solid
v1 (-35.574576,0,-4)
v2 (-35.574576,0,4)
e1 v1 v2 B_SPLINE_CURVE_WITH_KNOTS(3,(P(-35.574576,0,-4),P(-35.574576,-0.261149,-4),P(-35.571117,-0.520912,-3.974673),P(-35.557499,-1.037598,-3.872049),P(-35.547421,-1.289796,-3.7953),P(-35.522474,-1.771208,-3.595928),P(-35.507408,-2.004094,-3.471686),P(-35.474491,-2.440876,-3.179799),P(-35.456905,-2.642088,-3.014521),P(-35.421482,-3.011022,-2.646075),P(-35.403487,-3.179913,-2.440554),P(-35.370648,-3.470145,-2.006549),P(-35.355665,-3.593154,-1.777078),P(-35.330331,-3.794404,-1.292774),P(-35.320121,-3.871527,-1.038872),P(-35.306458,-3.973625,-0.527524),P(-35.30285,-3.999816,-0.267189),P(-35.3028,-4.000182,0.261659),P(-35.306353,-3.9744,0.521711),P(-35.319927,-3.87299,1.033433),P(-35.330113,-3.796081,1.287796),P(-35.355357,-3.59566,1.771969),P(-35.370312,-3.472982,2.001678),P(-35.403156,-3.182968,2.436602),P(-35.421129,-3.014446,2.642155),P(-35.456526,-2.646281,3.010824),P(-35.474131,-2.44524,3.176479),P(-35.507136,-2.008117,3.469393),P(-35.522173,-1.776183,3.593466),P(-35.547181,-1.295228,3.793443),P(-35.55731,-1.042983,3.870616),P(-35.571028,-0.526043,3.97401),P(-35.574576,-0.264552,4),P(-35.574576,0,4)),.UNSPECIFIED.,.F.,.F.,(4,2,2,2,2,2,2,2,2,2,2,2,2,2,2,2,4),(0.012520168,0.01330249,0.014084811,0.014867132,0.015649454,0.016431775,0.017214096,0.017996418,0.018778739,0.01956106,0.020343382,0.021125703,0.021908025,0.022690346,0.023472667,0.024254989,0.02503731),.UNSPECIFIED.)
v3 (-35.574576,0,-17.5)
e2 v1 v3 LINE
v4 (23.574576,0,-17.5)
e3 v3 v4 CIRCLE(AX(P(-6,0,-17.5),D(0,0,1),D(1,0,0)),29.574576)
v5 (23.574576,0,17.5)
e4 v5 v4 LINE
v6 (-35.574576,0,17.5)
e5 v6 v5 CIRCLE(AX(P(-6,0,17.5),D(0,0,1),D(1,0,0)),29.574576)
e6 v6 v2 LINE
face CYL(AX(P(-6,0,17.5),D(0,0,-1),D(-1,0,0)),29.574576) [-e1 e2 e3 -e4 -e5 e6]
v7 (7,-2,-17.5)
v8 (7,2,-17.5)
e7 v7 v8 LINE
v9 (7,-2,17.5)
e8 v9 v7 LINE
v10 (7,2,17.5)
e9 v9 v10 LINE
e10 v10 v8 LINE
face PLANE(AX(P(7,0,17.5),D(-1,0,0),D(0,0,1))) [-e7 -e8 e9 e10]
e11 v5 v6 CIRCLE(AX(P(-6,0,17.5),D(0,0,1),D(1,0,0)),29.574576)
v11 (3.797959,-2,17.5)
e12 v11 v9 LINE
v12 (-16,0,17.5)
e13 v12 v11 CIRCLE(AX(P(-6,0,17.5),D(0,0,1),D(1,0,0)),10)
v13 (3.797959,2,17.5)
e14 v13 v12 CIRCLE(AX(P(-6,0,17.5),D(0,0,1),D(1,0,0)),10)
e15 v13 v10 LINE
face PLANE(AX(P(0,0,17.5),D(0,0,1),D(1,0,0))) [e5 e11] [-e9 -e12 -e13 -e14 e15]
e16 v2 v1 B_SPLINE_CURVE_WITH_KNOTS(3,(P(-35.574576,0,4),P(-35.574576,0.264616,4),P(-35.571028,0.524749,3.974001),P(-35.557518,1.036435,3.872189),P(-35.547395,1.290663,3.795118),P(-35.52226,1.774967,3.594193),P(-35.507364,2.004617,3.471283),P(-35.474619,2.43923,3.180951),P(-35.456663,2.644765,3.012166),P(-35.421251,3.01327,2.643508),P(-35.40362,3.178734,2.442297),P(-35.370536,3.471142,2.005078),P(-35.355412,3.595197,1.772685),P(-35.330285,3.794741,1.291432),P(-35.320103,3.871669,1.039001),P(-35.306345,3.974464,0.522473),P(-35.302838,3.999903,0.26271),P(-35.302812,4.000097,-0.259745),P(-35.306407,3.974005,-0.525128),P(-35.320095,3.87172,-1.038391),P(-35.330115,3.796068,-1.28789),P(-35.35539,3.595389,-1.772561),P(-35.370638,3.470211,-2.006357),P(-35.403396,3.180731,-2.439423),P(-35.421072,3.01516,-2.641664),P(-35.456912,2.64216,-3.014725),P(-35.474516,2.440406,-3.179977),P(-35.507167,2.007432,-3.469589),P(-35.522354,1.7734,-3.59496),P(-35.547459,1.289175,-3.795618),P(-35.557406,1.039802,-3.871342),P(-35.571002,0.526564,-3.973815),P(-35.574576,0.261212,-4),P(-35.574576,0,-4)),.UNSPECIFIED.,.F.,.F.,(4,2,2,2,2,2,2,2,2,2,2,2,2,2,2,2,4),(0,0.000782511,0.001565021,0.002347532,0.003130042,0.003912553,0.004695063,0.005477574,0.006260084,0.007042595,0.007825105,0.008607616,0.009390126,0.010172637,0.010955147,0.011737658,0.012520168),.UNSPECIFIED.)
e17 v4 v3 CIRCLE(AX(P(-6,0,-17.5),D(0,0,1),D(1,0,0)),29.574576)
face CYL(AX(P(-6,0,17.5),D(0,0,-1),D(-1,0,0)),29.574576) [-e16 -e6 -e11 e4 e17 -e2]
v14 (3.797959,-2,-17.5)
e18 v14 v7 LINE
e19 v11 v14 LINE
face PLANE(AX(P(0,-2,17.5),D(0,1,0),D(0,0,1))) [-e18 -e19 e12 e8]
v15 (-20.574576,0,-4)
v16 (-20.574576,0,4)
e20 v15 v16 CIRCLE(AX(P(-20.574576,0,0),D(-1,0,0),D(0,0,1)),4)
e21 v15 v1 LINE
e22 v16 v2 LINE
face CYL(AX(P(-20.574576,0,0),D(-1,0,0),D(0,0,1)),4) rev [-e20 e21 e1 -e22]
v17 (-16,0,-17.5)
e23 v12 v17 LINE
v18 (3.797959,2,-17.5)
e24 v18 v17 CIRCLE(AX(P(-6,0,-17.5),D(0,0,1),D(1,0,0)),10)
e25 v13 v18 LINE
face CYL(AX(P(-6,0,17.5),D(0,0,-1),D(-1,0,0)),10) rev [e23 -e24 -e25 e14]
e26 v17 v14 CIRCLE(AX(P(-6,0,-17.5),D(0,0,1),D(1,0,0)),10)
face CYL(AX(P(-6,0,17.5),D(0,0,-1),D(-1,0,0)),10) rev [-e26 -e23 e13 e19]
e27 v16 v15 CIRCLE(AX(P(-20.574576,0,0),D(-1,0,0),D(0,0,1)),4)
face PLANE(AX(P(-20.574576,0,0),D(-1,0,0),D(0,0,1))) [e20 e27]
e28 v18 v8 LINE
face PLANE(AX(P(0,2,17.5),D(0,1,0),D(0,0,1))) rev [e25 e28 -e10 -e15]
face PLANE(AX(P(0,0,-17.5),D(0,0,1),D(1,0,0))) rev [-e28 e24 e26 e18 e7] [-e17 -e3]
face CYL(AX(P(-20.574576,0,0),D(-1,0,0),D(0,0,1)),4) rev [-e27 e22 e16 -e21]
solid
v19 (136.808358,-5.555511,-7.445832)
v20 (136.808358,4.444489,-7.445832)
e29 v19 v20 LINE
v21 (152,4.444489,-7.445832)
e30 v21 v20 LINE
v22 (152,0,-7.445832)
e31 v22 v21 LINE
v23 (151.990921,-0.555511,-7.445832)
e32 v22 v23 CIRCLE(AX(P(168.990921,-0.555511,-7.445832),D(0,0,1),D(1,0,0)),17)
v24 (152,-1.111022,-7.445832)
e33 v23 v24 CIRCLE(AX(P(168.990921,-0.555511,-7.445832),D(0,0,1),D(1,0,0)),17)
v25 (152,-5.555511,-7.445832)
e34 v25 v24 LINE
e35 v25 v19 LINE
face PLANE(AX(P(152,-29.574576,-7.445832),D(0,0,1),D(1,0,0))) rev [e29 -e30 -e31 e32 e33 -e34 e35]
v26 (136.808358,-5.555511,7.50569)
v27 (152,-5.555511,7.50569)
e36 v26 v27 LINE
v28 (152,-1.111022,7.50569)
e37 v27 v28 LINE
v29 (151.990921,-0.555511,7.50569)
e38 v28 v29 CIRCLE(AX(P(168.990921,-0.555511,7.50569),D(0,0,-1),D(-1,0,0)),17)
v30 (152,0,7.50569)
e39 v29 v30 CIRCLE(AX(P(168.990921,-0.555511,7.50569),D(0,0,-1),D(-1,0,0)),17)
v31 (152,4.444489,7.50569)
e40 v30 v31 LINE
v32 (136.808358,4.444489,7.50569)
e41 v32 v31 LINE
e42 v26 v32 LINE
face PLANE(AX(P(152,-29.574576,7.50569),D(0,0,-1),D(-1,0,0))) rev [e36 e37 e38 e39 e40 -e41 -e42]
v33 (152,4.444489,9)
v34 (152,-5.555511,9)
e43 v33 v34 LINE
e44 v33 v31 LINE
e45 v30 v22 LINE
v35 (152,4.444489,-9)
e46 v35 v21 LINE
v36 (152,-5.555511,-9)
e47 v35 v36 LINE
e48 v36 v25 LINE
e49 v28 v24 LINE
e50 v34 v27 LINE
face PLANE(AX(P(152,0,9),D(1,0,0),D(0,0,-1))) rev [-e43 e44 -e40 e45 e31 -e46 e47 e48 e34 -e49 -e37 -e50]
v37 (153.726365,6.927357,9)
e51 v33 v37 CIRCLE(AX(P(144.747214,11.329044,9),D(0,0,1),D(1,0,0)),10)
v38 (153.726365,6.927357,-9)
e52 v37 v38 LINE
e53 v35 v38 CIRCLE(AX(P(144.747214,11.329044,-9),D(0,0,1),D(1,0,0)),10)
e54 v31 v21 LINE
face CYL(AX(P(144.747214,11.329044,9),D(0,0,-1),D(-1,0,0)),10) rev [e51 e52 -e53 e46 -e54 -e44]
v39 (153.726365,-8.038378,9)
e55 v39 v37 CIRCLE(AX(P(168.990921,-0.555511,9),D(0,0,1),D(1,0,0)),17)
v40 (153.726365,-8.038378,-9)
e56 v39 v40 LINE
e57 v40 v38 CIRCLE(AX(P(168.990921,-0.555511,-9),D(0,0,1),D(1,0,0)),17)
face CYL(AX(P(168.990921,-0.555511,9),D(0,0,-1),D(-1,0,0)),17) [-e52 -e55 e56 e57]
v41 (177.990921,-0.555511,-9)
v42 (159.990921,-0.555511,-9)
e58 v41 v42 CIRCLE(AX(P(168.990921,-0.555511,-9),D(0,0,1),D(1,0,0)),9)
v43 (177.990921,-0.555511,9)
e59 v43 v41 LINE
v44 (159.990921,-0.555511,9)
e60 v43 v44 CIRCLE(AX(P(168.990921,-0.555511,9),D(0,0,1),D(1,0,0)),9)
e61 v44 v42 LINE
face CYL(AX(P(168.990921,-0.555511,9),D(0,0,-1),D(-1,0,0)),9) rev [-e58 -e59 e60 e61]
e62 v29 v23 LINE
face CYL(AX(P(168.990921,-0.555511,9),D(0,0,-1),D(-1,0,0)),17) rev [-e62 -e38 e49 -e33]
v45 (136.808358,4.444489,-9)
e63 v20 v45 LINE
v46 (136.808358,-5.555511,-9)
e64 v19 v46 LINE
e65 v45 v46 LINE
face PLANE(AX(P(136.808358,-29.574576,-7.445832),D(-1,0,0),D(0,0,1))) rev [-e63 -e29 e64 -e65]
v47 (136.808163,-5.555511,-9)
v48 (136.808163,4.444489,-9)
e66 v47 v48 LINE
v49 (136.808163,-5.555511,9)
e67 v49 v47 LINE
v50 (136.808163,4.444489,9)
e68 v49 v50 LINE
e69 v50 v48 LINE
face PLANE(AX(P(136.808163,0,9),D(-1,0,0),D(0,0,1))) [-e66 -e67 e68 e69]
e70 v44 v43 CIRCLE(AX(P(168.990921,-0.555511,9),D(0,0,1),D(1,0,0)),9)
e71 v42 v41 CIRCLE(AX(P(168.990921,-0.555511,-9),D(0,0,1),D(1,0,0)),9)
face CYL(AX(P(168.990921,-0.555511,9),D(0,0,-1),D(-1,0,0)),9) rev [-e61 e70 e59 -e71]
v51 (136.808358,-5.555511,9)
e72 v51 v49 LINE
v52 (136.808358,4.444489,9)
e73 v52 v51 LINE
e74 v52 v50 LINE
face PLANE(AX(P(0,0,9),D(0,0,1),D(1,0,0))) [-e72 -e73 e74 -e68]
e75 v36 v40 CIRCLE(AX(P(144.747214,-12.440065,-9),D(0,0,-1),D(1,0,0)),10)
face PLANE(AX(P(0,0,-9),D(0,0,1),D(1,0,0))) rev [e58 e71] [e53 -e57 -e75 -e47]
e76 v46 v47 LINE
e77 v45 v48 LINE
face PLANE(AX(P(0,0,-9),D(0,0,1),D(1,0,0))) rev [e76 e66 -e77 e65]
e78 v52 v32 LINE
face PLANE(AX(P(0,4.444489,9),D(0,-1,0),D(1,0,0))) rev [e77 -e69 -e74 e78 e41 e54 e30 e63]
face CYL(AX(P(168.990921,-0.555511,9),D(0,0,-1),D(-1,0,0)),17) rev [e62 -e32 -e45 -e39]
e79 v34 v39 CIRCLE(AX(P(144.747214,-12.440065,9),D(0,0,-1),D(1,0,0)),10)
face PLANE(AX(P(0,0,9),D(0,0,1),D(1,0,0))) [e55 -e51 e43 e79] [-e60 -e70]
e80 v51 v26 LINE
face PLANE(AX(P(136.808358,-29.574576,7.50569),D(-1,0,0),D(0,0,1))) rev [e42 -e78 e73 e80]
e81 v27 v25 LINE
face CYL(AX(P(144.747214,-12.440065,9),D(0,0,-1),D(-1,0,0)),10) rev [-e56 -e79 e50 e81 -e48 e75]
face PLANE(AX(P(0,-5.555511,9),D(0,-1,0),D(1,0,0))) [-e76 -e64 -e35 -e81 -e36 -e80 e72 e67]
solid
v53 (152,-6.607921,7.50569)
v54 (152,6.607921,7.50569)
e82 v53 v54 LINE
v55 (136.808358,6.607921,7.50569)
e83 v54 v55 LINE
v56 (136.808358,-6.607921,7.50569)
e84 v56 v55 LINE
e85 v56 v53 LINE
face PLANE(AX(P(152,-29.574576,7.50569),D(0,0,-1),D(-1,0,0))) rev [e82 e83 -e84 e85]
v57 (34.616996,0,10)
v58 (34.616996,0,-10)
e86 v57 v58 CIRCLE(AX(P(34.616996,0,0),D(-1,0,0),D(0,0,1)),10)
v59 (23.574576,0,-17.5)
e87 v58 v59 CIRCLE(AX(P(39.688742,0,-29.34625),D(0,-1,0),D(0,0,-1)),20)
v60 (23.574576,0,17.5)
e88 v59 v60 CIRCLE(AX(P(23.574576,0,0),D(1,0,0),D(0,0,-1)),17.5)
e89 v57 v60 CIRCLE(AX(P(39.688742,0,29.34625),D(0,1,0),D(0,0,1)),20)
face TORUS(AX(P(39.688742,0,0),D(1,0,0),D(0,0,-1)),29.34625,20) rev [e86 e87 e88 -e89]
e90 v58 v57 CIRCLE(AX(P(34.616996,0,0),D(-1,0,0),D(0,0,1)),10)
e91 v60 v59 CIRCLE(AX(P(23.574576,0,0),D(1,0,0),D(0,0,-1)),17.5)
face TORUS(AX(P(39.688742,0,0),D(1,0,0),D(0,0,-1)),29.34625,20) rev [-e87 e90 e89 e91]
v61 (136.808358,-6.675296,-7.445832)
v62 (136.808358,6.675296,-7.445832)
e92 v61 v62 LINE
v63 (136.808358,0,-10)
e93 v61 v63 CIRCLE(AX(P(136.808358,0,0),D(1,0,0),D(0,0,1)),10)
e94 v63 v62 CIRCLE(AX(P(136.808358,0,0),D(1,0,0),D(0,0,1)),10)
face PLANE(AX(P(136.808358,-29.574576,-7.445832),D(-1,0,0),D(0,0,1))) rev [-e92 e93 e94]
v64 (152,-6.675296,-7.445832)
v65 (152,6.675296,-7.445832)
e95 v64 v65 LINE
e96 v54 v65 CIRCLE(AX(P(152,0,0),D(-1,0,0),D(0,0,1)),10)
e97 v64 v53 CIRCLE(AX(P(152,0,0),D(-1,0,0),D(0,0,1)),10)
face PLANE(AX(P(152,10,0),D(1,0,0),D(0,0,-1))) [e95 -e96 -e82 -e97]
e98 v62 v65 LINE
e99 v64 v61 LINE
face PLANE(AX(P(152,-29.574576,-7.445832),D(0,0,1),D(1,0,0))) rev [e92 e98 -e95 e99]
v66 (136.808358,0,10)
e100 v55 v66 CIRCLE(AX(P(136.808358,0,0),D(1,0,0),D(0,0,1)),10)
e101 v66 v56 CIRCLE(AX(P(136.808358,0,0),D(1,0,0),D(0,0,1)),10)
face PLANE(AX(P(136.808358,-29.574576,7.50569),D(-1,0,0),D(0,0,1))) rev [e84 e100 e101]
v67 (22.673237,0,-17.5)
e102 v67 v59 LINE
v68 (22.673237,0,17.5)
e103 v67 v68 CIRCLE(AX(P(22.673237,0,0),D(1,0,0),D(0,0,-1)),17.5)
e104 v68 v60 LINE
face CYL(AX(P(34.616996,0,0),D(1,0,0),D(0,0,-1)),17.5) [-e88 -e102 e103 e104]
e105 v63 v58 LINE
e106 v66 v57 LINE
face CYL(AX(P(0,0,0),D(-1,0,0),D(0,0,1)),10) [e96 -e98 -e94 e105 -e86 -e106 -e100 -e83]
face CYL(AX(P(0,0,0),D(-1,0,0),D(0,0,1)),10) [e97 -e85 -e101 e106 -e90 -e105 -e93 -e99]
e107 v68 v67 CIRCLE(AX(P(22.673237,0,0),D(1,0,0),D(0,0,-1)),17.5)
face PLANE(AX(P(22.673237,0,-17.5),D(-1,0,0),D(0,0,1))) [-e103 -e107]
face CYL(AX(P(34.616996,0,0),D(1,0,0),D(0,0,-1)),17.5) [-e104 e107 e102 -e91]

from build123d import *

# Parameters (mm, degrees)
ROD_SHANK_PROFILE_W           = 117.383003688
ROD_SHANK_PROFILE_H           = 10
BIG_END_EYE_PROFILE_R         = 29.574575968
BIG_END_EYE_DEPTH             = 17.5
SMALL_END_EYE_DEPTH           = 9
SMALL_END_FLAT_CUT_DEPTH      = 190.138912872
SMALL_END_FLAT_CUT_DEPTH_BACK = 190.138912872
SMALL_END_FLAT_PROFILE_W      = 15.191641878
SMALL_END_FLAT_PROFILE_H      = 5.882566039
SMALL_END_FLAT_PROFILE_H_2    = 8.578742141
BIG_END_HUB_PROFILE_W         = 15
BIG_END_HUB_PROFILE_H         = 4
BIG_END_KEYWAY_PROFILE_R      = 4
BIG_END_KEYWAY_CUT_DEPTH      = 15


with BuildPart() as part:
    # Rod Shank Profile → Rod Shank (revolve)
    with BuildSketch(Plane.XY, mode=Mode.PRIVATE) as rod_shank_sk:
        with Locations((93.308498156, 5)):
            Rectangle(ROD_SHANK_PROFILE_W, ROD_SHANK_PROFILE_H)
    revolve(rod_shank_sk.sketch.rotate(Axis((0, 0, 0), (1, 0, 0)), 90), axis=Axis((0, 0, 0), (1, 0, 0)))

    # Big End Neck Profile → Big End Neck (revolve)
    with BuildSketch(Plane(origin=(0, 0, 0), x_dir=(1, 0, 0), z_dir=(0, 1, 0))):
        with BuildLine():
            Line((34.616996312, 10), (34.616996312, 0))
            Line((34.616996312, 0), (23.574575968, 0))
            Line((23.574575968, 0), (22.673236665, 0))
            Line((22.673236665, 0), (22.673236665, 17.5))
            Line((22.673236665, 17.5), (23.574575968, 17.5))
            ThreePointArc((23.574575968, 17.5), (28.451606539, 12.801559743), (34.616996312, 10))
        make_face()
    revolve(axis=Axis((34.616996312, 0, 0), (-1, 0, 0)))


with BuildPart() as body_2:
    # Big End Eye Profile → Big End Eye (new, symmetric)
    with BuildSketch(Plane.XY):
        with Locations((-6, 0)):
            Circle(BIG_END_EYE_PROFILE_R)
        with BuildLine():
            ThreePointArc((3.797958971, 2), (-16, 0), (3.797958971, -2))
            Line((3.797958971, -2), (7, -2))
            Line((7, -2), (7, 2))
            Line((7, 2), (3.797958971, 2))
        make_face(mode=Mode.SUBTRACT)
    extrude(amount=BIG_END_EYE_DEPTH, both=True)

    # Big End Hub Profile → Big End Hub (revolve)
    with BuildSketch(Plane(origin=(0, 0, 0), x_dir=(1, 0, 0), z_dir=(0, 1, 0))):
        with Locations((-28.074575968, 2)):
            Rectangle(BIG_END_HUB_PROFILE_W, BIG_END_HUB_PROFILE_H)
    revolve(axis=Axis((-35.574575968, 0, 0), (1, 0, 0)))

    # Big End Keyway Profile → Big End Keyway Cut (cut)
    with BuildSketch(Plane.ZY.offset(35.574575968)):
        Circle(BIG_END_KEYWAY_PROFILE_R)
    extrude(amount=-BIG_END_KEYWAY_CUT_DEPTH, mode=Mode.SUBTRACT)


with BuildPart() as body_3:
    # Small End Eye Profile → Small End Eye (new, symmetric)
    # profile 1 of 2: a face of its own
    with BuildSketch(Plane.XY):
        with BuildLine():
            Line((152, -1.111021517), (152, -5.555510758))
            ThreePointArc((152, -5.555510758), (152.957579332, -6.731309244), (153.726364566, -8.038378301))
            ThreePointArc((153.726364566, -8.038378301), (185.990921335, -0.555510758), (153.726364566, 6.927356785))
            ThreePointArc((153.726364566, 6.927356785), (152.957579332, 5.620287727), (152, 4.444489242))
            Line((152, 4.444489242), (152, 0))
            Line((152, 0), (152, -1.111021517))
        make_face()
        with BuildLine():
            ThreePointArc((161.507606561, -5.555510758), (166.378435254, 8.056975322), (177.990921335, -0.555510758))
            ThreePointArc((177.990921335, -0.555510758), (171.603407415, -9.167996839), (161.507606561, -5.555510758))
        make_face(mode=Mode.SUBTRACT)
    # profile 2 of 2: a face of its own
    with BuildSketch(Plane.XY):
        with BuildLine():
            Line((136.808163002, -5.555510758), (152, -5.555510758))
            Line((152, -5.555510758), (152, -1.111021517))
            ThreePointArc((152, -1.111021517), (151.990921335, -0.555510758), (152, 0))
            Line((152, 0), (152, 4.444489242))
            Line((152, 4.444489242), (136.808163002, 4.444489242))
            Line((136.808163002, 4.444489242), (136.808163002, -5.555510758))
        make_face()
    extrude(amount=SMALL_END_EYE_DEPTH, both=True)


with BuildPart() as small_end_flat_cut_tool:
    # Small End Flat Profile → Small End Flat Cut (new, two sides: drawn at the far end of the back side and taken through both)
    with BuildSketch(Plane(origin=(0, 0, 0), x_dir=(1, 0, 0), z_dir=(0, 1, 0)).offset(-SMALL_END_FLAT_CUT_DEPTH_BACK)):
        with Locations((144.404179061, -10.446972753)):
            Rectangle(SMALL_END_FLAT_PROFILE_W, SMALL_END_FLAT_PROFILE_H)
        with Locations((144.404179061, 11.735203356)):
            Rectangle(SMALL_END_FLAT_PROFILE_W, SMALL_END_FLAT_PROFILE_H_2)
    extrude(amount=SMALL_END_FLAT_CUT_DEPTH + SMALL_END_FLAT_CUT_DEPTH_BACK)


with BuildPart() as part_1:
    add(part.part)

    # Small End Flat Cut: cut by small_end_flat_cut_tool
    add(small_end_flat_cut_tool.part, mode=Mode.SUBTRACT)


with BuildPart() as body_3_1:
    add(body_3.part)

    # Small End Flat Cut: cut by small_end_flat_cut_tool
    add(small_end_flat_cut_tool.part, mode=Mode.SUBTRACT)


solid = Compound([body_2.part, part_1.part, body_3_1.part])
